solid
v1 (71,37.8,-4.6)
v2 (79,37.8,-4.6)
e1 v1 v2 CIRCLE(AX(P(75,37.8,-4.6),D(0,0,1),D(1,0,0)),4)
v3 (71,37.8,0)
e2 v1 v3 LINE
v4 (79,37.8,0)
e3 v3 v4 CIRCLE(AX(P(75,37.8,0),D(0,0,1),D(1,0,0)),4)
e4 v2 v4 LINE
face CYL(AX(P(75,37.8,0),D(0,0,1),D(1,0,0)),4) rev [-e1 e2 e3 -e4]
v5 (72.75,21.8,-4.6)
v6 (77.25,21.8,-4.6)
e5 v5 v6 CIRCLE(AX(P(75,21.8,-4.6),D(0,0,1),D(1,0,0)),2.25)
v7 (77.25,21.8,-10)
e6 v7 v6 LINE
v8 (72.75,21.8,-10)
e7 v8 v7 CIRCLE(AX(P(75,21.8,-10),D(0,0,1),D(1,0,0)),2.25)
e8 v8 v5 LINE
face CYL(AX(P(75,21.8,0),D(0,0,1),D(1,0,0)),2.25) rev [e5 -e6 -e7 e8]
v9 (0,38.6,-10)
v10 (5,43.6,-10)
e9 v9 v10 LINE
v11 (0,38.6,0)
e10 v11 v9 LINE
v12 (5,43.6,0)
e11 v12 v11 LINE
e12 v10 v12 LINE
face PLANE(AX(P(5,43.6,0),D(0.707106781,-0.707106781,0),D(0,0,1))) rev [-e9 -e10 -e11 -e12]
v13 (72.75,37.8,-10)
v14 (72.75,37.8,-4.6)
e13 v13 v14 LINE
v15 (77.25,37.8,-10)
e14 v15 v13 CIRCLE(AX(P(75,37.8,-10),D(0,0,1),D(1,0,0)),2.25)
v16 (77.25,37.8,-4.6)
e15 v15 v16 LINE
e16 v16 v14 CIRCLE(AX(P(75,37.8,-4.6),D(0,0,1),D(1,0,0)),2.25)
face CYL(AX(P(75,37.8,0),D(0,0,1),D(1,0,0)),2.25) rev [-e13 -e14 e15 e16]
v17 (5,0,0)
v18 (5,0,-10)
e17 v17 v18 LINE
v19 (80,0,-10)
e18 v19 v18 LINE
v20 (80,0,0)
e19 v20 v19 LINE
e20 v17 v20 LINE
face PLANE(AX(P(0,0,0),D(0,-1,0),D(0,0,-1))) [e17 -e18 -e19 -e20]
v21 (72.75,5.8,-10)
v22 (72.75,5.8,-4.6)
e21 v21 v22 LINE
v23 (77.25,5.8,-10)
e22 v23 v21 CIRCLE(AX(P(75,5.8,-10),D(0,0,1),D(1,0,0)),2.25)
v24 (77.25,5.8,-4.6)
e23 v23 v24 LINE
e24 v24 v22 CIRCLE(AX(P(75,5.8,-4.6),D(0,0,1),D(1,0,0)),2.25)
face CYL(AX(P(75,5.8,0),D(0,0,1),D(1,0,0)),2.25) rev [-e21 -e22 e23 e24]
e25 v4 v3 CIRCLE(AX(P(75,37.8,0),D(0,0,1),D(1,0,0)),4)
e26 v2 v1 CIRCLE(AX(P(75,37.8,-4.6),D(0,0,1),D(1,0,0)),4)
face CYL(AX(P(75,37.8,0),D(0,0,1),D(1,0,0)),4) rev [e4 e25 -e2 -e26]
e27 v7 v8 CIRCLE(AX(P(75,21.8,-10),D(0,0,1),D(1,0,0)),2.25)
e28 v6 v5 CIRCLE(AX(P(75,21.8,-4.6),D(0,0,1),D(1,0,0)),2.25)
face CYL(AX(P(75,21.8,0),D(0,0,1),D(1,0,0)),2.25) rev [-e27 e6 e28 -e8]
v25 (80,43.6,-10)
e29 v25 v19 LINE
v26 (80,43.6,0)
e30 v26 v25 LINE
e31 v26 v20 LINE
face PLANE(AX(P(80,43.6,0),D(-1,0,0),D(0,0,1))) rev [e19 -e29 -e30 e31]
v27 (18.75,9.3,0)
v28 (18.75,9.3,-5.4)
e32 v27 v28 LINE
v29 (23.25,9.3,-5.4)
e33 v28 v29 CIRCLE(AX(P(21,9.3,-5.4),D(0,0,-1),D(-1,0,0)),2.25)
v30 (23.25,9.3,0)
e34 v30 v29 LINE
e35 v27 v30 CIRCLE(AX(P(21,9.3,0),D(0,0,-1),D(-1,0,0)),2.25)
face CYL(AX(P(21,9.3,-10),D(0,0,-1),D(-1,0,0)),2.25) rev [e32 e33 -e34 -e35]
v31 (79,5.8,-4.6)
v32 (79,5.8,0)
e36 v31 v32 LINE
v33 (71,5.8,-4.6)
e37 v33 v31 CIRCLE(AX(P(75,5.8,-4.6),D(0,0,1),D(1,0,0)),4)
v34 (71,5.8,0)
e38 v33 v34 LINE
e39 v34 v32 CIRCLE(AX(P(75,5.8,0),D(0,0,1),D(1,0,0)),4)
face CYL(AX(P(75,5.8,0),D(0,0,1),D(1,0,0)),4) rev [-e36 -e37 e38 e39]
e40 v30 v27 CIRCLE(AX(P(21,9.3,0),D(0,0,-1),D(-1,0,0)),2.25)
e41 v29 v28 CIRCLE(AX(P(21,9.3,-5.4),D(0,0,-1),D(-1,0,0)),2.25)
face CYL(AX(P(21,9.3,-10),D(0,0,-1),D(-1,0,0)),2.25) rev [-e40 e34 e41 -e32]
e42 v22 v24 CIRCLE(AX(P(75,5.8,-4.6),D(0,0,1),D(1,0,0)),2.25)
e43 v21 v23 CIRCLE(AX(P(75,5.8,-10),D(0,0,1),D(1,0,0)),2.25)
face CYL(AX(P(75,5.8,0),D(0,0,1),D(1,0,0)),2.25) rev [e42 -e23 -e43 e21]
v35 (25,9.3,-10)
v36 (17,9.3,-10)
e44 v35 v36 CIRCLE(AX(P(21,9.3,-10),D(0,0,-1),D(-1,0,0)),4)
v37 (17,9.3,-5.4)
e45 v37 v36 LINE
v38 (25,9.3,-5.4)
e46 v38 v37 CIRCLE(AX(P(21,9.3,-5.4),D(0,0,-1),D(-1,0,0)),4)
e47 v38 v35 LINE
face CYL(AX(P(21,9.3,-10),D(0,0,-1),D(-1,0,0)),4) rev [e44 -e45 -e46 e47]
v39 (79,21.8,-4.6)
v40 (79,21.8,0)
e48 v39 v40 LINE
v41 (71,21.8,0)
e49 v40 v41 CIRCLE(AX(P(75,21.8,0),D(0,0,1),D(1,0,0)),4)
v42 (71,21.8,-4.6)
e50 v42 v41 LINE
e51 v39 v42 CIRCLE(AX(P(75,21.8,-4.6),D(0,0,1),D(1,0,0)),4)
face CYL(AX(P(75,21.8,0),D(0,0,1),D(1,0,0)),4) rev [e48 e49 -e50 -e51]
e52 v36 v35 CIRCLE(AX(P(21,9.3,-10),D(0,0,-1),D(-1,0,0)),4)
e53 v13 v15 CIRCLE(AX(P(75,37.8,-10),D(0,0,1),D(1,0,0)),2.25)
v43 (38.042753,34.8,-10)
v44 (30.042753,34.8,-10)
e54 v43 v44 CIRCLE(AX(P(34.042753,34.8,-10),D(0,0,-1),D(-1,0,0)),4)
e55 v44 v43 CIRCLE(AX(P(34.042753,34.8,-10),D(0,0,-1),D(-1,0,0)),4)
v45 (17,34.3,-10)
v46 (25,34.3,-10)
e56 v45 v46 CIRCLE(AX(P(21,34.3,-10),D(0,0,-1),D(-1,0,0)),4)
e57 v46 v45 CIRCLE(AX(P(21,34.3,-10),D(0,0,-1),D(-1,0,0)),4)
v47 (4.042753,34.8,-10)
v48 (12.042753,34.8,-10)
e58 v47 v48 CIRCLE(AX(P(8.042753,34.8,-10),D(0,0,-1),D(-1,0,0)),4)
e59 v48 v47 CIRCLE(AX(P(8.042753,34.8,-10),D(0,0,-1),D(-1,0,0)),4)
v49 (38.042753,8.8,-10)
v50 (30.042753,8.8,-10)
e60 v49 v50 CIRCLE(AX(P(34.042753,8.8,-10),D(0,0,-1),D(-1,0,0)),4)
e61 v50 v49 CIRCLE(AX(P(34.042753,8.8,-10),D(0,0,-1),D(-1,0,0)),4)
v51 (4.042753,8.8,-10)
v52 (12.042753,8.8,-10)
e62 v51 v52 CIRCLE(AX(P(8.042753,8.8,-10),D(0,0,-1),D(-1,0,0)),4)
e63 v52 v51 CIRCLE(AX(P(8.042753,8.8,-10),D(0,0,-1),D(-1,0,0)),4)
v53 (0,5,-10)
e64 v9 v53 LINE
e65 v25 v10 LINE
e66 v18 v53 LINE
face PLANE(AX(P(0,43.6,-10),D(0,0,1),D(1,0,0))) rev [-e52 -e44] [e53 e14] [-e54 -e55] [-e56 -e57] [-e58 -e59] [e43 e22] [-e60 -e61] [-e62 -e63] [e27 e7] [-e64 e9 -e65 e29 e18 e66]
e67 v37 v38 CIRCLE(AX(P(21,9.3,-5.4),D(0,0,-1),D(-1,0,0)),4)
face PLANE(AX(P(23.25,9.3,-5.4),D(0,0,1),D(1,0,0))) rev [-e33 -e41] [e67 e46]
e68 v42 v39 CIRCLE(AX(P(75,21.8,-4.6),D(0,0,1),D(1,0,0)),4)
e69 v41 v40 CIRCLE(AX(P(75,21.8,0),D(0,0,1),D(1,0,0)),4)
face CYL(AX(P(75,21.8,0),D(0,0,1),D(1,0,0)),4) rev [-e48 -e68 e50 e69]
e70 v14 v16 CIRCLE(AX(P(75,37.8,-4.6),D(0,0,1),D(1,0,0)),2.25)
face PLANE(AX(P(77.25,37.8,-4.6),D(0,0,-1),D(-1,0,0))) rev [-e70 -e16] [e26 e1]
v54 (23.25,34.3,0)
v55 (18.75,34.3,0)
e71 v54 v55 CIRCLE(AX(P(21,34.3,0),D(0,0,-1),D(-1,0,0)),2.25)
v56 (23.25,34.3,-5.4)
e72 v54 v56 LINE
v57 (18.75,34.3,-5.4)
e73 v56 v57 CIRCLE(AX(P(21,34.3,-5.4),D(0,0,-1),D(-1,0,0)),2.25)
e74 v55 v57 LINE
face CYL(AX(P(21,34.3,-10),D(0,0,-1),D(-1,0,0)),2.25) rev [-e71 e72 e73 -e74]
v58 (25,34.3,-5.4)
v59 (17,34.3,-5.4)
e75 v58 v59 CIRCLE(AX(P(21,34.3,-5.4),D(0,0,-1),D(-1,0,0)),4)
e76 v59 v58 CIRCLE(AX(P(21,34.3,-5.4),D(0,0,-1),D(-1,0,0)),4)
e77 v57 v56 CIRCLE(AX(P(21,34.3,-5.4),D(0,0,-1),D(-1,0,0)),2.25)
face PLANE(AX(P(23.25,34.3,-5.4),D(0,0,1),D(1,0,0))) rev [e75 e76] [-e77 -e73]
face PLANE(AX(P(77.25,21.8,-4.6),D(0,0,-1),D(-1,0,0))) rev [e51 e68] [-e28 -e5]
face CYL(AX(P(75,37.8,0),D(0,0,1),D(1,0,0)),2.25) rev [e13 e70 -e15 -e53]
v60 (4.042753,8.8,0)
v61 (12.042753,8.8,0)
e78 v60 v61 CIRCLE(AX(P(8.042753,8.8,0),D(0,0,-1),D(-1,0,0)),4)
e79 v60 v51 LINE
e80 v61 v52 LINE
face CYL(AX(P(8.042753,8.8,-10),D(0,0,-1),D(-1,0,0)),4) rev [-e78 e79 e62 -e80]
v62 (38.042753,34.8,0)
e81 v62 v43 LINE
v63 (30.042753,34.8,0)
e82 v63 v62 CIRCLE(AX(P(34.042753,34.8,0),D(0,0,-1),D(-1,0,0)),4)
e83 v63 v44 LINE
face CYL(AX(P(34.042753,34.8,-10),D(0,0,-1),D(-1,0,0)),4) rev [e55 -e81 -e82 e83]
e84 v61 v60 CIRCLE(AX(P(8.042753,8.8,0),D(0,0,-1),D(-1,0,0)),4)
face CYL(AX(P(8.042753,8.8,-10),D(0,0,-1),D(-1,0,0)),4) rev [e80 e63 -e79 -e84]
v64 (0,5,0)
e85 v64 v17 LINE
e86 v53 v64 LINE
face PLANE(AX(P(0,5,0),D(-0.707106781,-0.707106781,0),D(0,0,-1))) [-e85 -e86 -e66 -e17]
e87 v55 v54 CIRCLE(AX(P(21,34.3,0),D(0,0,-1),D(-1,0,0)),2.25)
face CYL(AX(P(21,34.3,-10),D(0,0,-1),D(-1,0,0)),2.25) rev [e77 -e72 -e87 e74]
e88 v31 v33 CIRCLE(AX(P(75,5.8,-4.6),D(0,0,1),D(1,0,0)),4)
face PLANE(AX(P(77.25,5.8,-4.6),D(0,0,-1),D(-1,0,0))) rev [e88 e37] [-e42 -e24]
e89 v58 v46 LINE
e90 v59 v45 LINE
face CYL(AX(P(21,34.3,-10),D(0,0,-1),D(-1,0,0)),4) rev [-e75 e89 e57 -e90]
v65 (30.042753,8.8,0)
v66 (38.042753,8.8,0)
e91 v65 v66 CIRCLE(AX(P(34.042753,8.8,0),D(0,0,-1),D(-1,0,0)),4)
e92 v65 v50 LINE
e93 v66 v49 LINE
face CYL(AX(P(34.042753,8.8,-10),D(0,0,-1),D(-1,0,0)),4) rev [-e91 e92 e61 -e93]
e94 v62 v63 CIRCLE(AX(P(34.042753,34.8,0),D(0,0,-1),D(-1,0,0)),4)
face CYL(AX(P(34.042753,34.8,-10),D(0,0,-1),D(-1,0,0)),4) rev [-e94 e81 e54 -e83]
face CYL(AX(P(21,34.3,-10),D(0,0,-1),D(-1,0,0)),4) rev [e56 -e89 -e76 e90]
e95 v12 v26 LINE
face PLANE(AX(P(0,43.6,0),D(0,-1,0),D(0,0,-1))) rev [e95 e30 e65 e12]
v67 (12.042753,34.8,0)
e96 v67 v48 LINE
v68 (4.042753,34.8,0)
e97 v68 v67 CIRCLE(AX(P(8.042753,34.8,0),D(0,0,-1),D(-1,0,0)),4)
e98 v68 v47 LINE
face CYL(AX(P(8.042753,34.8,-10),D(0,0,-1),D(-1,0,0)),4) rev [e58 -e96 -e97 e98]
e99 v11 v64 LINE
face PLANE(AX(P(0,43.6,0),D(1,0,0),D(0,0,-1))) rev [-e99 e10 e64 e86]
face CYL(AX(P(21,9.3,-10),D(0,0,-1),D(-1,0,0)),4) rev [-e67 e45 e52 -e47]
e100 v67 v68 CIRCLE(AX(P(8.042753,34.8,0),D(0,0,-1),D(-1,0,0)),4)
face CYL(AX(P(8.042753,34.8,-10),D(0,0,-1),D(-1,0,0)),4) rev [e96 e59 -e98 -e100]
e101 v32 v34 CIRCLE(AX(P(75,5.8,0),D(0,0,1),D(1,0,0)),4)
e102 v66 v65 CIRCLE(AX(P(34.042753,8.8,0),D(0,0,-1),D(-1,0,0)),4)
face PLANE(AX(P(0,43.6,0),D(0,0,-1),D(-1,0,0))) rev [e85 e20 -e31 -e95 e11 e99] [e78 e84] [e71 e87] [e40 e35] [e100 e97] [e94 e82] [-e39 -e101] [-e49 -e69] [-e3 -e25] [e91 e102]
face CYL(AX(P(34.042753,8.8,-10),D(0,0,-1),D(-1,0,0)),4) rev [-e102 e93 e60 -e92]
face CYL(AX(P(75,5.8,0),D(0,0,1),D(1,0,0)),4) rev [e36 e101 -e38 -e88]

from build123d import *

# Parameters (mm, degrees)
SKETCH_1_W                   = 80
SKETCH_1_H                   = 10
EXTRUDE_1_DEPTH              = 43.6
CHAMFER_1_SIZE               = 5
HOLE_WIZARD_8_0_8_1_D        = 8
HOLE_WIZARD_M4_1_D           = 4.5
HOLE_WIZARD_M4_1_CBORE_D     = 8
HOLE_WIZARD_M4_1_CBORE_DEPTH = 4.6
HOLE_WIZARD_M4_2_D           = 4.5
HOLE_WIZARD_M4_2_CBORE_D     = 8
HOLE_WIZARD_M4_2_CBORE_DEPTH = 4.6


with BuildPart() as part:
    # 草图1 → 凸台-拉伸1 (new body)
    with BuildSketch(Plane(origin=(0, 0, 0), x_dir=(1, 0, 0), z_dir=(0, 1, 0))):
        with Locations((40, 5)):
            Rectangle(SKETCH_1_W, SKETCH_1_H)
    extrude(amount=EXTRUDE_1_DEPTH)

    # 倒角1
    chamfer_1_edges = [part.edges().sort_by_distance(p)[0] for p in [
        (0, 43.6, -5),
        (0, 0, -5),
    ]]
    chamfer(chamfer_1_edges, length=CHAMFER_1_SIZE)

    # Ø8.0 (8) 直径孔1 (through all)
    with Locations(Plane(origin=(0, 0, -10), x_dir=(-1, 0, 0), z_dir=(0, 0, -1))):
        with Locations((-34.042753413, 34.8), (-8.042753413, 34.8), (-8.042753413, 8.8), (-34.042753413, 8.8)):
            Hole(HOLE_WIZARD_8_0_8_1_D / 2)

    # M4 六角圆柱头螺钉的柱形沉头孔1 (through all)
    with Locations(Plane(origin=(0, 0, -10), x_dir=(-1, 0, 0), z_dir=(0, 0, -1))):
        with Locations((-21, 34.3), (-21, 9.3)):
            CounterBoreHole(HOLE_WIZARD_M4_1_D / 2, HOLE_WIZARD_M4_1_CBORE_D / 2, HOLE_WIZARD_M4_1_CBORE_DEPTH)

    # M4 六角圆柱头螺钉的柱形沉头孔2 (through all)
    with Locations(Plane.XY):
        with Locations((75, 37.8), (75, 5.8), (75, 21.8)):
            CounterBoreHole(HOLE_WIZARD_M4_2_D / 2, HOLE_WIZARD_M4_2_CBORE_D / 2, HOLE_WIZARD_M4_2_CBORE_DEPTH)


solid = part.part
